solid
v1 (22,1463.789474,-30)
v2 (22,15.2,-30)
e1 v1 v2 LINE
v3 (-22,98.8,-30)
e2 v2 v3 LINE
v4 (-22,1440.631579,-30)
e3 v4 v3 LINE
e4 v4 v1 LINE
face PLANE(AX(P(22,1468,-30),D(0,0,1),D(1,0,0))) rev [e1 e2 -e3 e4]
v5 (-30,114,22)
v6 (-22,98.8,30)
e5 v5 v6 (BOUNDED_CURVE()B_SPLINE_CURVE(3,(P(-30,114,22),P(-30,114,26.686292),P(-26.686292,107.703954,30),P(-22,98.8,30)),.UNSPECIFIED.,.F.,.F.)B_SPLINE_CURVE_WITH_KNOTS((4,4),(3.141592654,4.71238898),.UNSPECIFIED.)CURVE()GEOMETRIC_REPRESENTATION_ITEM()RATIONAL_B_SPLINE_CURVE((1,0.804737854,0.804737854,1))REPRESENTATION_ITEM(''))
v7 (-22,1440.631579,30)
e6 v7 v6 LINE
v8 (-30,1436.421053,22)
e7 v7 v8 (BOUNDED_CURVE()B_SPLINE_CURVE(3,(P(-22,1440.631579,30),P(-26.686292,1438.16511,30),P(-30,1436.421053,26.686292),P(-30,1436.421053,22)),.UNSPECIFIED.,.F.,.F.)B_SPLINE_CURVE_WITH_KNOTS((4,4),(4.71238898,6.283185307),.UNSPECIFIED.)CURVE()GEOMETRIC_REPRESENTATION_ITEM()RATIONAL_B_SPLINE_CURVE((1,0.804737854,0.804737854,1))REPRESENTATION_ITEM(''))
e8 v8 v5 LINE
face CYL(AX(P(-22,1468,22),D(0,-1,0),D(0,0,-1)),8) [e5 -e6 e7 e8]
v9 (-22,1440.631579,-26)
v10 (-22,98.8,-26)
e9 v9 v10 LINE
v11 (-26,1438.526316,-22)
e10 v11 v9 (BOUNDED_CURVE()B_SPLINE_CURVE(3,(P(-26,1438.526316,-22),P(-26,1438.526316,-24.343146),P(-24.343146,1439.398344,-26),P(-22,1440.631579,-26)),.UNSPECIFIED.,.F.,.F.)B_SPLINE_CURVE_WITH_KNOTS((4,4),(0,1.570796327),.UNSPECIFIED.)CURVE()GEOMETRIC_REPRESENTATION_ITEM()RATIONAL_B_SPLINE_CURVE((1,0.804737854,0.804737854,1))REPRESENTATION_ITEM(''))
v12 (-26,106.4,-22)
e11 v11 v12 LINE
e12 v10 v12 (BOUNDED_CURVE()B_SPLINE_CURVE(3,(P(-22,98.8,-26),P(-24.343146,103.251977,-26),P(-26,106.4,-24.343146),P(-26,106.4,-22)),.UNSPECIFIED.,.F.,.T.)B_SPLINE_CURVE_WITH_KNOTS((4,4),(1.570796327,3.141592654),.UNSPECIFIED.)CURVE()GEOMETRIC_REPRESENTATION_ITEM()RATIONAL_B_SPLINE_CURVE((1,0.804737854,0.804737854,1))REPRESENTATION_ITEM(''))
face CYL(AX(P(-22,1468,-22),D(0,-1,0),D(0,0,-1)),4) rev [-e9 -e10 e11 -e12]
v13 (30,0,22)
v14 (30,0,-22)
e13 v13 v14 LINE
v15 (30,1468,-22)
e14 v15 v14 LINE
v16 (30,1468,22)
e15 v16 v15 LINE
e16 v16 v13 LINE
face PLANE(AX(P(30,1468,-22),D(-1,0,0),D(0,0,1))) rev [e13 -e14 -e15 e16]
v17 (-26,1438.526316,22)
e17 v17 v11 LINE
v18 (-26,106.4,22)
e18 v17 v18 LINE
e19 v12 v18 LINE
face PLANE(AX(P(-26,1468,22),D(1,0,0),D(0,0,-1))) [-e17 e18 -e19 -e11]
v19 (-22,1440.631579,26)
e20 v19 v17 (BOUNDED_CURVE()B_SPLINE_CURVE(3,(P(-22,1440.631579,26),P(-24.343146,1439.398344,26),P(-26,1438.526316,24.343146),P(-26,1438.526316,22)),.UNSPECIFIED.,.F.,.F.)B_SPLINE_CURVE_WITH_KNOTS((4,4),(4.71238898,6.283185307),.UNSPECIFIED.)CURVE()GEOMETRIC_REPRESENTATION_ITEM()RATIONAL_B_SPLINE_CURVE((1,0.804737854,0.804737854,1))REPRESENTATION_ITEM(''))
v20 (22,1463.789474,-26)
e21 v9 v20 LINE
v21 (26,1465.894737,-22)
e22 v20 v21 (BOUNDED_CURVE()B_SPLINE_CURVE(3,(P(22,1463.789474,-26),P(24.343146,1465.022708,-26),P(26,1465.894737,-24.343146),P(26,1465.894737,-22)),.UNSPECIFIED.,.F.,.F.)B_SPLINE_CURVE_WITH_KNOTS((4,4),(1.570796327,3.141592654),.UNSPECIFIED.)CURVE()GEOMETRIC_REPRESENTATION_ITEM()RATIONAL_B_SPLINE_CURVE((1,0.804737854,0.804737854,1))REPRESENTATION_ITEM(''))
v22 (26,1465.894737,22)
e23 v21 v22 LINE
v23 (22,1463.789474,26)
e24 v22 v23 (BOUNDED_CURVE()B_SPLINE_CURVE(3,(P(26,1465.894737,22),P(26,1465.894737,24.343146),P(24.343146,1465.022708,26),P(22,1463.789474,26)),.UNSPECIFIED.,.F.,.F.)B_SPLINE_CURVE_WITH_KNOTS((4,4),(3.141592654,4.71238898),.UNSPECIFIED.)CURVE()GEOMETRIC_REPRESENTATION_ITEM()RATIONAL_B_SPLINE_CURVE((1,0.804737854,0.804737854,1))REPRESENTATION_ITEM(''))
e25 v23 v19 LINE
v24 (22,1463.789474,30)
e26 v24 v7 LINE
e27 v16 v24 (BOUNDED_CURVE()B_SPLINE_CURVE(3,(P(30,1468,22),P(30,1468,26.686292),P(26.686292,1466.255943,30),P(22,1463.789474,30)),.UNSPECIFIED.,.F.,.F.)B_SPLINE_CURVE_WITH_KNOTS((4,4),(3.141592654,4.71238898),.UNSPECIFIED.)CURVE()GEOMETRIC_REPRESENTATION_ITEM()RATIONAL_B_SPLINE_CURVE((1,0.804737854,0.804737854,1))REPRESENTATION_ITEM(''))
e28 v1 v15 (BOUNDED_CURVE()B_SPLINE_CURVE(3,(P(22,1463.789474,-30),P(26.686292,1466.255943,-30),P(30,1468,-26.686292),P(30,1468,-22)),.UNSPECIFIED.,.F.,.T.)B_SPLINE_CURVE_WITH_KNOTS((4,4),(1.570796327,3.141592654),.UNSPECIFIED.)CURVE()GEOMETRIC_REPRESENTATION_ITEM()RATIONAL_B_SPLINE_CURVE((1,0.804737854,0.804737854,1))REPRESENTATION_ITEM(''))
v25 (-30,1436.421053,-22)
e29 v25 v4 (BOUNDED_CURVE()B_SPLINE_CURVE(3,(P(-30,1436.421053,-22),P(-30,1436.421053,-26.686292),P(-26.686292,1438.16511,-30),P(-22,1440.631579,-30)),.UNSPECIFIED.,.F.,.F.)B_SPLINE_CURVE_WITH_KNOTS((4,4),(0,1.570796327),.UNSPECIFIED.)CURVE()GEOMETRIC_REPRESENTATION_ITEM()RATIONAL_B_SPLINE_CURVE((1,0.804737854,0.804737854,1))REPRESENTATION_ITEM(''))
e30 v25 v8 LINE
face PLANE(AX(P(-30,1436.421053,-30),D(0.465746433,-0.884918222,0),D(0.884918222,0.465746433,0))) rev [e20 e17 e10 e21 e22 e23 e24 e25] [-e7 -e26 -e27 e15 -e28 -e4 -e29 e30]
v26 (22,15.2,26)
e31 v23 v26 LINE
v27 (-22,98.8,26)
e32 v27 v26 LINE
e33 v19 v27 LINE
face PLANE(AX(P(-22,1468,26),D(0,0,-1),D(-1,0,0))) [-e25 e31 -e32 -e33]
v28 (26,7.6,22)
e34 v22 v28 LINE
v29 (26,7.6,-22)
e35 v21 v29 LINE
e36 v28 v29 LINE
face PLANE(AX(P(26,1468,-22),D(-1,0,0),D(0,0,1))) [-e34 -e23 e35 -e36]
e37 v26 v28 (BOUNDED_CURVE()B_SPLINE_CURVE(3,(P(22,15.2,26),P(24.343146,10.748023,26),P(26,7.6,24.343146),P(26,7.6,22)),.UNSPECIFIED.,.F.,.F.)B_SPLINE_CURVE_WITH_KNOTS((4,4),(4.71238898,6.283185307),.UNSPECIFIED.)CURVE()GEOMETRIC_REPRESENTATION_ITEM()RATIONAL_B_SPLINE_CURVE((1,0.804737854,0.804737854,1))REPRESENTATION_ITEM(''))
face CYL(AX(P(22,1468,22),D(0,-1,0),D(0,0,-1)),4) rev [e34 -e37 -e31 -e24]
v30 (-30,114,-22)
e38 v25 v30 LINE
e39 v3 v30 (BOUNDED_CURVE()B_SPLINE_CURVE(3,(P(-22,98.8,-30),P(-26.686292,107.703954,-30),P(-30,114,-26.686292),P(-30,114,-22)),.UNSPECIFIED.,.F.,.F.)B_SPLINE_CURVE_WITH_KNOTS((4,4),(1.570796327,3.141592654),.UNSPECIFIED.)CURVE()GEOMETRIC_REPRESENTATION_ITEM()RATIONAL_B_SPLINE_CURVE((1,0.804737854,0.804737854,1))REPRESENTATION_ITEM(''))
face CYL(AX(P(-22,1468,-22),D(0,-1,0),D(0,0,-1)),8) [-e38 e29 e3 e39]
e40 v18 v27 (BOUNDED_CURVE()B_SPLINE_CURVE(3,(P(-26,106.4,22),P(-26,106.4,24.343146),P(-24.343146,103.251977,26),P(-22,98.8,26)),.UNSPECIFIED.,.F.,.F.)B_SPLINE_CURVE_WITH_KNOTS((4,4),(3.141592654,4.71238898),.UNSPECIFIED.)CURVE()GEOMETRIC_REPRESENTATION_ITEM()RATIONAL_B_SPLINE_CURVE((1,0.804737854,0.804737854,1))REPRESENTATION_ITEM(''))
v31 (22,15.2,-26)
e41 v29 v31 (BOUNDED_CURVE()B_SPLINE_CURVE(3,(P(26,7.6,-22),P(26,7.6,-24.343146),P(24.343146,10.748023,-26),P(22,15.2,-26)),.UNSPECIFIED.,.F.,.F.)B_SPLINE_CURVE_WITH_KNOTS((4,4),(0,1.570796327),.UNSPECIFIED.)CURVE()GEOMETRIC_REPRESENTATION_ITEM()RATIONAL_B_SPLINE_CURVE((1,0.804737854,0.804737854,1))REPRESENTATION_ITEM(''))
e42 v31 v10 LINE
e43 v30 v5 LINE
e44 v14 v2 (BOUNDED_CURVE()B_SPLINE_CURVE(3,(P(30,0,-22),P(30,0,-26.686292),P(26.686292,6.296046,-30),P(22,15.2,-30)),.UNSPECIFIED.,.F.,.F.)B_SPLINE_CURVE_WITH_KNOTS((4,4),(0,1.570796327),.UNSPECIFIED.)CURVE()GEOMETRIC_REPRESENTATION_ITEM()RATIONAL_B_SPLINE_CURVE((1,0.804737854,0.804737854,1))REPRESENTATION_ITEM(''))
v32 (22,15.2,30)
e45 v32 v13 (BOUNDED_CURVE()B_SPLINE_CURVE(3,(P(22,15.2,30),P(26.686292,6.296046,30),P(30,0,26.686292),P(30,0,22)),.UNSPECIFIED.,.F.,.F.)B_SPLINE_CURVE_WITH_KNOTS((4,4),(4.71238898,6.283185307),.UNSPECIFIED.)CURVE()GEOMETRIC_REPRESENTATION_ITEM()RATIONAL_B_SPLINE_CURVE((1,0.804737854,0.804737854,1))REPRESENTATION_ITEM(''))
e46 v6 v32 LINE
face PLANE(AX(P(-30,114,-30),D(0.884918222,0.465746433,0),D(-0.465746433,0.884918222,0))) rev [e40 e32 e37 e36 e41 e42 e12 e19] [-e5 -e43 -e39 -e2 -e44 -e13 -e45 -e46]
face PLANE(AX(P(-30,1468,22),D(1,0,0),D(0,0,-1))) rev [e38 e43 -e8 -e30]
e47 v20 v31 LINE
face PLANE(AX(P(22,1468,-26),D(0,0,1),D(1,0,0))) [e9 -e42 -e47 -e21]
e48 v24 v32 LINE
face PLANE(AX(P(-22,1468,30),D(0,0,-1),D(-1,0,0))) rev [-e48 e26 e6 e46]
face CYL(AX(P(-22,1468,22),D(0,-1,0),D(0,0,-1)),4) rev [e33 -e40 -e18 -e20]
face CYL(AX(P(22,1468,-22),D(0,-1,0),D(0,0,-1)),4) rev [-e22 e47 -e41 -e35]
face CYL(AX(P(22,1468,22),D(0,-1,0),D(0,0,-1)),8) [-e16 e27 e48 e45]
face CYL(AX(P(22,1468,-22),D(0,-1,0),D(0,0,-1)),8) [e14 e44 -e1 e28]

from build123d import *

# Parameters (mm, degrees)
GB_T_6728_2002_SQUARE_HOLLOW_SECTION_60_DEPTH = 1468
CUT_EXTRUDE1_DEPTH                            = 1470.531898259
CUT_EXTRUDE1_DEPTH_BACK                       = 1470.531898259


with BuildPart() as part:
    # Sketch1 → GB/T 6728-2002 square hollow section 60×60×4(1) (new body)
    with BuildSketch(Plane(origin=(0, 0, 0), x_dir=(-1, 0, 0), z_dir=(0, 1, 0))):
        with BuildLine():
            Line((-22, -30), (22, -30))
            ThreePointArc((22, -30), (27.656854249, -27.656854249), (30, -22))
            Line((30, -22), (30, 22))
            ThreePointArc((30, 22), (27.656854249, 27.656854249), (22, 30))
            Line((22, 30), (-22, 30))
            ThreePointArc((-22, 30), (-27.656854249, 27.656854249), (-30, 22))
            Line((-30, 22), (-30, -22))
            ThreePointArc((-30, -22), (-27.656854249, -27.656854249), (-22, -30))
        make_face()
        with BuildLine():
            Line((-22, -26), (22, -26))
            ThreePointArc((22, -26), (24.828427125, -24.828427125), (26, -22))
            Line((26, -22), (26, 22))
            ThreePointArc((26, 22), (24.828427125, 24.828427125), (22, 26))
            Line((22, 26), (-22, 26))
            ThreePointArc((-22, 26), (-24.828427125, 24.828427125), (-26, 22))
            Line((-26, 22), (-26, -22))
            ThreePointArc((-26, -22), (-24.828427125, -24.828427125), (-22, -26))
        make_face(mode=Mode.SUBTRACT)
    extrude(amount=GB_T_6728_2002_SQUARE_HOLLOW_SECTION_60_DEPTH)

    # Sketch2 → Cut-Extrude1 (cut, two sides: drawn at the far end of the back side and taken through both)
    with BuildSketch(Plane.XY.offset(30).offset(-CUT_EXTRUDE1_DEPTH_BACK)):
        Polygon((-30, 0), (-30, 114), (30, 0), align=None)
        Polygon((-30, 1436.421052632), (30, 1468), (-30, 1468), align=None)
    extrude(amount=CUT_EXTRUDE1_DEPTH + CUT_EXTRUDE1_DEPTH_BACK, mode=Mode.SUBTRACT)


solid = part.part
